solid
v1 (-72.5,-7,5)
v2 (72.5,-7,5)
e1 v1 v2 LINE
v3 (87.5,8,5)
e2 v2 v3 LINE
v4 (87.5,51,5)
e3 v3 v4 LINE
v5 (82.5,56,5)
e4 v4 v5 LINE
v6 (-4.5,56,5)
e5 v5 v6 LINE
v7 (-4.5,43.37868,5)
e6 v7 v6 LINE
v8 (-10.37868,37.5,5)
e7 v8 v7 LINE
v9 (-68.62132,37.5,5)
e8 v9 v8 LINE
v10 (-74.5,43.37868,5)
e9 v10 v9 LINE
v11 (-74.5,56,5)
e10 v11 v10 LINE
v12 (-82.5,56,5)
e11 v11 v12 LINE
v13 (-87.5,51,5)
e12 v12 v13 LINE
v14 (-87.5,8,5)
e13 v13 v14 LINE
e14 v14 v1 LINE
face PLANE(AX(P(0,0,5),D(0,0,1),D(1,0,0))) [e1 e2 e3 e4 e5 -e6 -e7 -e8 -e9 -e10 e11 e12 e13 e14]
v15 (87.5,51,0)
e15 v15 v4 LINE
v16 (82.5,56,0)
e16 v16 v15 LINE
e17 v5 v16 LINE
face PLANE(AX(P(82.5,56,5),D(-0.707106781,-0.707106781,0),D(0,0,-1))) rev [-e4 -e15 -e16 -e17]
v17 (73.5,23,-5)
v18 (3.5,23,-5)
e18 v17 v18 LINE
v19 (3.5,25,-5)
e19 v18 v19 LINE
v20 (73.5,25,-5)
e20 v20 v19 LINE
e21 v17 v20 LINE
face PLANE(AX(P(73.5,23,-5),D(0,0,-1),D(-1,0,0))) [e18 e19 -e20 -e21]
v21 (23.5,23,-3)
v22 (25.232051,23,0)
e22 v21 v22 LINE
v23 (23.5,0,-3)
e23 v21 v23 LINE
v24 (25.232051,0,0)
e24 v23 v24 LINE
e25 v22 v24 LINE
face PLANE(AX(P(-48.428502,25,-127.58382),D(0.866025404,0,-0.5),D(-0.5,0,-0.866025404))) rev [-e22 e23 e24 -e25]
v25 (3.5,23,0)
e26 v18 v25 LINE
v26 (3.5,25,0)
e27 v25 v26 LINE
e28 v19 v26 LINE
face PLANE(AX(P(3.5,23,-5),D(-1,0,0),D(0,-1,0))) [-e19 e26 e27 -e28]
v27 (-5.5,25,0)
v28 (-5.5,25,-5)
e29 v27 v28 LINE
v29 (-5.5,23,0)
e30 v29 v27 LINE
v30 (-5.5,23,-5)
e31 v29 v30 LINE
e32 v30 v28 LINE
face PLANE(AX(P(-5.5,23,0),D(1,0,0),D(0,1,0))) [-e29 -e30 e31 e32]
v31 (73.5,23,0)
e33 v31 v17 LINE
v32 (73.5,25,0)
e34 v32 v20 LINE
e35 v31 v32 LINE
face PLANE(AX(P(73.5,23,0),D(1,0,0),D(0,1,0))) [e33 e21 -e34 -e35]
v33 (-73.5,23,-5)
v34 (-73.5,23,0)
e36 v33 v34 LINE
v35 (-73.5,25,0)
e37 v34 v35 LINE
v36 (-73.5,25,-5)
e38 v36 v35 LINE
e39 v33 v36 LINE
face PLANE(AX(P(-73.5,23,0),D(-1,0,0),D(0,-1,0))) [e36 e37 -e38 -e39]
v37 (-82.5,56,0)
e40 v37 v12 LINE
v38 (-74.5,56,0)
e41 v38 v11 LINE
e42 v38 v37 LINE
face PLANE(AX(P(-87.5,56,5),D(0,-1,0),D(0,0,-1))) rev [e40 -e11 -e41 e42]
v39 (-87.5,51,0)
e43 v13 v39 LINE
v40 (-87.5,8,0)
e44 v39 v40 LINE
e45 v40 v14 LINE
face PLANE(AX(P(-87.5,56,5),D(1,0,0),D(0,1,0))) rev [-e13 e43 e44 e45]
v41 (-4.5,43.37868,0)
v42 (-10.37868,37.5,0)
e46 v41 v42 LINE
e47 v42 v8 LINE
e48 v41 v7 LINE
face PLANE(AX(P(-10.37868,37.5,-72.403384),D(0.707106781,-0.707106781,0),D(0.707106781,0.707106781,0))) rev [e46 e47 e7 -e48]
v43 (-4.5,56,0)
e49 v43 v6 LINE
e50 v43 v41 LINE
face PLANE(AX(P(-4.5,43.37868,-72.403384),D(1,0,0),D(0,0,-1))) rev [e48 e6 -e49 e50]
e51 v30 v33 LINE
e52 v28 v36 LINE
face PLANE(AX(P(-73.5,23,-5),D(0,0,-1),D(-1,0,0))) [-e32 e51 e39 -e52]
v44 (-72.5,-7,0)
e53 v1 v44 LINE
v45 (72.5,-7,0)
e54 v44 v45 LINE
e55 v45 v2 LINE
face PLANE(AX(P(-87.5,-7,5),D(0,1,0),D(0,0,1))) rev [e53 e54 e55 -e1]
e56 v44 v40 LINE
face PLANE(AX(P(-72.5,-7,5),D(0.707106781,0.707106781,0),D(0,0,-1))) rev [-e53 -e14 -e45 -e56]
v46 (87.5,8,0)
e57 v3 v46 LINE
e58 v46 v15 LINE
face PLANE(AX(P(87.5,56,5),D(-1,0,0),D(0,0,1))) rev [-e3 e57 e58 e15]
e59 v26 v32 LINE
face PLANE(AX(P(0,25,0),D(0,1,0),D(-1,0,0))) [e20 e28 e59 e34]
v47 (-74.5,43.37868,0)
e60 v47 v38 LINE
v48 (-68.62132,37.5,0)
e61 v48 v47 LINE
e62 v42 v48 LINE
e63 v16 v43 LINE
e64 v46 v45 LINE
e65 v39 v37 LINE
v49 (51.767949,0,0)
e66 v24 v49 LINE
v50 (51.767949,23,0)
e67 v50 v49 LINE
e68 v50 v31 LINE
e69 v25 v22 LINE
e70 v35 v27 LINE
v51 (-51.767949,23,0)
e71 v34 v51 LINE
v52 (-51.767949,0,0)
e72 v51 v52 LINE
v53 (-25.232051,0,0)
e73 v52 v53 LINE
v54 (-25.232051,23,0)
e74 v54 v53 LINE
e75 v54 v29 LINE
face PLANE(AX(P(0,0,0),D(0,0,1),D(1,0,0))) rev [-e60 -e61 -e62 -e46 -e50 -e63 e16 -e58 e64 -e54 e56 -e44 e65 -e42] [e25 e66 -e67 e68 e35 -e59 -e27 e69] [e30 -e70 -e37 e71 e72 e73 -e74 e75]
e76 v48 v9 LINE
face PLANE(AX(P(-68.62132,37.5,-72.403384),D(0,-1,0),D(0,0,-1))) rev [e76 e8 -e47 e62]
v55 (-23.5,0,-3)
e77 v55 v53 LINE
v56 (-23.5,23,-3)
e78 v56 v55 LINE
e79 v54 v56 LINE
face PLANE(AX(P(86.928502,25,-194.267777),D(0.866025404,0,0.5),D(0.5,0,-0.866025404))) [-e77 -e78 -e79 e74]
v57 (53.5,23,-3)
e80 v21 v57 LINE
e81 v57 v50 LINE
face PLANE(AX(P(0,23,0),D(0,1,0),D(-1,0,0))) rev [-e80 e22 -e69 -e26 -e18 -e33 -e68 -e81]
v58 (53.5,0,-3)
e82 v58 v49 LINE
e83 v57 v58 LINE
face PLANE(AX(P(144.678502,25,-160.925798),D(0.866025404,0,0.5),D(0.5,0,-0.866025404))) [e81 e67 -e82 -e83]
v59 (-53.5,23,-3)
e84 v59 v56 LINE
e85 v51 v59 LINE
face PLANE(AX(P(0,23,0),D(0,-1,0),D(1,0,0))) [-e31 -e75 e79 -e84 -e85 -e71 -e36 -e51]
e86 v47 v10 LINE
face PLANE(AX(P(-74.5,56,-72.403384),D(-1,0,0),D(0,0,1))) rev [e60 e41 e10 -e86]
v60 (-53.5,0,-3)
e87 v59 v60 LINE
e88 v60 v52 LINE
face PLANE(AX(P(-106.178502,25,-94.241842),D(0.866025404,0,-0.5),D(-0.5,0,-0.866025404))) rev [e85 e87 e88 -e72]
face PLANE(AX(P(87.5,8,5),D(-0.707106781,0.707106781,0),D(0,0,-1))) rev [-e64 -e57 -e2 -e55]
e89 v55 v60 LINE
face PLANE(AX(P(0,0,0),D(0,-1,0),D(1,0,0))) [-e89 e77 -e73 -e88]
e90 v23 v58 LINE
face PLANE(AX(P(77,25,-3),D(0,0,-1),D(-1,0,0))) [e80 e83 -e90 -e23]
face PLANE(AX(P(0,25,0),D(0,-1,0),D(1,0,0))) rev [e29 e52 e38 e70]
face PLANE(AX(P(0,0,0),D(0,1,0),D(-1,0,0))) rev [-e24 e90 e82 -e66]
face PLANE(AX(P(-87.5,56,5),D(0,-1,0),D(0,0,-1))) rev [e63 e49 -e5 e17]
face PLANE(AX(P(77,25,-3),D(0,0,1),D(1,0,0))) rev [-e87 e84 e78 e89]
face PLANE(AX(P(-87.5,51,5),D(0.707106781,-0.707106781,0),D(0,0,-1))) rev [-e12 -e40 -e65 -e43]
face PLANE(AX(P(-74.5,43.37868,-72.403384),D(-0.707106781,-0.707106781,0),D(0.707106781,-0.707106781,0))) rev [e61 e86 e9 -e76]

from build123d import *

# Parameters (mm, degrees)
SKETCH1_W           = 175
SKETCH1_H           = 63
BOSS_EXTRUDE1_DEPTH = 5
CUT_EXTRUDE1_DEPTH  = 5
CHAMFER1_SIZE       = 15
CHAMFER2_SIZE       = 5
BOSS_EXTRUDE2_START = -7
BOSS_EXTRUDE2_DEPTH = 25
SKETCH4_W           = 68
SKETCH4_H           = 5
SKETCH4_W_2         = 70
BOSS_EXTRUDE3_DEPTH = 2


with BuildPart() as part:
    # Sketch1 → Boss-Extrude1 (new body)
    with BuildSketch(Plane.XY):
        with Locations((0, 24.5)):
            Rectangle(SKETCH1_W, SKETCH1_H)
    extrude(amount=BOSS_EXTRUDE1_DEPTH)

    # Sketch2 → Cut-Extrude1 (cut)
    with BuildSketch(Plane.XY.offset(5)):
        Polygon((-74.5, 56), (-4.5, 56), (-4.5, 43.378679656), (-10.378679656, 37.5), (-68.621320344, 37.5), (-74.5, 43.378679656), align=None)
    extrude(amount=-CUT_EXTRUDE1_DEPTH, mode=Mode.SUBTRACT)

    # Chamfer1
    chamfer1_edges = [part.edges().sort_by_distance(p)[0] for p in [
        (87.5, -7, 2.5),
        (-87.5, -7, 2.5),
    ]]
    chamfer(chamfer1_edges, length=CHAMFER1_SIZE)

    # Chamfer2
    chamfer2_edges = [part.edges().sort_by_distance(p)[0] for p in [
        (-87.5, 56, 2.5),
        (87.5, 56, 2.5),
    ]]
    chamfer(chamfer2_edges, length=CHAMFER2_SIZE)

    # Sketch3 → Boss-Extrude2 (add)
    with BuildSketch(Plane.XZ.offset(7).offset(BOSS_EXTRUDE2_START)):
        Polygon((51.767949192, 0), (25.232050808, 0), (23.5, -3), (53.5, -3), align=None)
        Polygon((-53.5, -3), (-23.5, -3), (-25.232050808, 0), (-51.767949192, 0), align=None)
    extrude(amount=-BOSS_EXTRUDE2_DEPTH)

    # Sketch4 → Boss-Extrude3 (add)
    with BuildSketch(Plane(origin=(0, 25, 0), x_dir=(1, 0, 0), z_dir=(0, 1, 0))):
        with Locations((-39.5, 2.5)):
            Rectangle(SKETCH4_W, SKETCH4_H)
        with Locations((38.5, 2.5)):
            Rectangle(SKETCH4_W_2, SKETCH4_H)
    extrude(amount=-BOSS_EXTRUDE3_DEPTH)


solid = part.part
